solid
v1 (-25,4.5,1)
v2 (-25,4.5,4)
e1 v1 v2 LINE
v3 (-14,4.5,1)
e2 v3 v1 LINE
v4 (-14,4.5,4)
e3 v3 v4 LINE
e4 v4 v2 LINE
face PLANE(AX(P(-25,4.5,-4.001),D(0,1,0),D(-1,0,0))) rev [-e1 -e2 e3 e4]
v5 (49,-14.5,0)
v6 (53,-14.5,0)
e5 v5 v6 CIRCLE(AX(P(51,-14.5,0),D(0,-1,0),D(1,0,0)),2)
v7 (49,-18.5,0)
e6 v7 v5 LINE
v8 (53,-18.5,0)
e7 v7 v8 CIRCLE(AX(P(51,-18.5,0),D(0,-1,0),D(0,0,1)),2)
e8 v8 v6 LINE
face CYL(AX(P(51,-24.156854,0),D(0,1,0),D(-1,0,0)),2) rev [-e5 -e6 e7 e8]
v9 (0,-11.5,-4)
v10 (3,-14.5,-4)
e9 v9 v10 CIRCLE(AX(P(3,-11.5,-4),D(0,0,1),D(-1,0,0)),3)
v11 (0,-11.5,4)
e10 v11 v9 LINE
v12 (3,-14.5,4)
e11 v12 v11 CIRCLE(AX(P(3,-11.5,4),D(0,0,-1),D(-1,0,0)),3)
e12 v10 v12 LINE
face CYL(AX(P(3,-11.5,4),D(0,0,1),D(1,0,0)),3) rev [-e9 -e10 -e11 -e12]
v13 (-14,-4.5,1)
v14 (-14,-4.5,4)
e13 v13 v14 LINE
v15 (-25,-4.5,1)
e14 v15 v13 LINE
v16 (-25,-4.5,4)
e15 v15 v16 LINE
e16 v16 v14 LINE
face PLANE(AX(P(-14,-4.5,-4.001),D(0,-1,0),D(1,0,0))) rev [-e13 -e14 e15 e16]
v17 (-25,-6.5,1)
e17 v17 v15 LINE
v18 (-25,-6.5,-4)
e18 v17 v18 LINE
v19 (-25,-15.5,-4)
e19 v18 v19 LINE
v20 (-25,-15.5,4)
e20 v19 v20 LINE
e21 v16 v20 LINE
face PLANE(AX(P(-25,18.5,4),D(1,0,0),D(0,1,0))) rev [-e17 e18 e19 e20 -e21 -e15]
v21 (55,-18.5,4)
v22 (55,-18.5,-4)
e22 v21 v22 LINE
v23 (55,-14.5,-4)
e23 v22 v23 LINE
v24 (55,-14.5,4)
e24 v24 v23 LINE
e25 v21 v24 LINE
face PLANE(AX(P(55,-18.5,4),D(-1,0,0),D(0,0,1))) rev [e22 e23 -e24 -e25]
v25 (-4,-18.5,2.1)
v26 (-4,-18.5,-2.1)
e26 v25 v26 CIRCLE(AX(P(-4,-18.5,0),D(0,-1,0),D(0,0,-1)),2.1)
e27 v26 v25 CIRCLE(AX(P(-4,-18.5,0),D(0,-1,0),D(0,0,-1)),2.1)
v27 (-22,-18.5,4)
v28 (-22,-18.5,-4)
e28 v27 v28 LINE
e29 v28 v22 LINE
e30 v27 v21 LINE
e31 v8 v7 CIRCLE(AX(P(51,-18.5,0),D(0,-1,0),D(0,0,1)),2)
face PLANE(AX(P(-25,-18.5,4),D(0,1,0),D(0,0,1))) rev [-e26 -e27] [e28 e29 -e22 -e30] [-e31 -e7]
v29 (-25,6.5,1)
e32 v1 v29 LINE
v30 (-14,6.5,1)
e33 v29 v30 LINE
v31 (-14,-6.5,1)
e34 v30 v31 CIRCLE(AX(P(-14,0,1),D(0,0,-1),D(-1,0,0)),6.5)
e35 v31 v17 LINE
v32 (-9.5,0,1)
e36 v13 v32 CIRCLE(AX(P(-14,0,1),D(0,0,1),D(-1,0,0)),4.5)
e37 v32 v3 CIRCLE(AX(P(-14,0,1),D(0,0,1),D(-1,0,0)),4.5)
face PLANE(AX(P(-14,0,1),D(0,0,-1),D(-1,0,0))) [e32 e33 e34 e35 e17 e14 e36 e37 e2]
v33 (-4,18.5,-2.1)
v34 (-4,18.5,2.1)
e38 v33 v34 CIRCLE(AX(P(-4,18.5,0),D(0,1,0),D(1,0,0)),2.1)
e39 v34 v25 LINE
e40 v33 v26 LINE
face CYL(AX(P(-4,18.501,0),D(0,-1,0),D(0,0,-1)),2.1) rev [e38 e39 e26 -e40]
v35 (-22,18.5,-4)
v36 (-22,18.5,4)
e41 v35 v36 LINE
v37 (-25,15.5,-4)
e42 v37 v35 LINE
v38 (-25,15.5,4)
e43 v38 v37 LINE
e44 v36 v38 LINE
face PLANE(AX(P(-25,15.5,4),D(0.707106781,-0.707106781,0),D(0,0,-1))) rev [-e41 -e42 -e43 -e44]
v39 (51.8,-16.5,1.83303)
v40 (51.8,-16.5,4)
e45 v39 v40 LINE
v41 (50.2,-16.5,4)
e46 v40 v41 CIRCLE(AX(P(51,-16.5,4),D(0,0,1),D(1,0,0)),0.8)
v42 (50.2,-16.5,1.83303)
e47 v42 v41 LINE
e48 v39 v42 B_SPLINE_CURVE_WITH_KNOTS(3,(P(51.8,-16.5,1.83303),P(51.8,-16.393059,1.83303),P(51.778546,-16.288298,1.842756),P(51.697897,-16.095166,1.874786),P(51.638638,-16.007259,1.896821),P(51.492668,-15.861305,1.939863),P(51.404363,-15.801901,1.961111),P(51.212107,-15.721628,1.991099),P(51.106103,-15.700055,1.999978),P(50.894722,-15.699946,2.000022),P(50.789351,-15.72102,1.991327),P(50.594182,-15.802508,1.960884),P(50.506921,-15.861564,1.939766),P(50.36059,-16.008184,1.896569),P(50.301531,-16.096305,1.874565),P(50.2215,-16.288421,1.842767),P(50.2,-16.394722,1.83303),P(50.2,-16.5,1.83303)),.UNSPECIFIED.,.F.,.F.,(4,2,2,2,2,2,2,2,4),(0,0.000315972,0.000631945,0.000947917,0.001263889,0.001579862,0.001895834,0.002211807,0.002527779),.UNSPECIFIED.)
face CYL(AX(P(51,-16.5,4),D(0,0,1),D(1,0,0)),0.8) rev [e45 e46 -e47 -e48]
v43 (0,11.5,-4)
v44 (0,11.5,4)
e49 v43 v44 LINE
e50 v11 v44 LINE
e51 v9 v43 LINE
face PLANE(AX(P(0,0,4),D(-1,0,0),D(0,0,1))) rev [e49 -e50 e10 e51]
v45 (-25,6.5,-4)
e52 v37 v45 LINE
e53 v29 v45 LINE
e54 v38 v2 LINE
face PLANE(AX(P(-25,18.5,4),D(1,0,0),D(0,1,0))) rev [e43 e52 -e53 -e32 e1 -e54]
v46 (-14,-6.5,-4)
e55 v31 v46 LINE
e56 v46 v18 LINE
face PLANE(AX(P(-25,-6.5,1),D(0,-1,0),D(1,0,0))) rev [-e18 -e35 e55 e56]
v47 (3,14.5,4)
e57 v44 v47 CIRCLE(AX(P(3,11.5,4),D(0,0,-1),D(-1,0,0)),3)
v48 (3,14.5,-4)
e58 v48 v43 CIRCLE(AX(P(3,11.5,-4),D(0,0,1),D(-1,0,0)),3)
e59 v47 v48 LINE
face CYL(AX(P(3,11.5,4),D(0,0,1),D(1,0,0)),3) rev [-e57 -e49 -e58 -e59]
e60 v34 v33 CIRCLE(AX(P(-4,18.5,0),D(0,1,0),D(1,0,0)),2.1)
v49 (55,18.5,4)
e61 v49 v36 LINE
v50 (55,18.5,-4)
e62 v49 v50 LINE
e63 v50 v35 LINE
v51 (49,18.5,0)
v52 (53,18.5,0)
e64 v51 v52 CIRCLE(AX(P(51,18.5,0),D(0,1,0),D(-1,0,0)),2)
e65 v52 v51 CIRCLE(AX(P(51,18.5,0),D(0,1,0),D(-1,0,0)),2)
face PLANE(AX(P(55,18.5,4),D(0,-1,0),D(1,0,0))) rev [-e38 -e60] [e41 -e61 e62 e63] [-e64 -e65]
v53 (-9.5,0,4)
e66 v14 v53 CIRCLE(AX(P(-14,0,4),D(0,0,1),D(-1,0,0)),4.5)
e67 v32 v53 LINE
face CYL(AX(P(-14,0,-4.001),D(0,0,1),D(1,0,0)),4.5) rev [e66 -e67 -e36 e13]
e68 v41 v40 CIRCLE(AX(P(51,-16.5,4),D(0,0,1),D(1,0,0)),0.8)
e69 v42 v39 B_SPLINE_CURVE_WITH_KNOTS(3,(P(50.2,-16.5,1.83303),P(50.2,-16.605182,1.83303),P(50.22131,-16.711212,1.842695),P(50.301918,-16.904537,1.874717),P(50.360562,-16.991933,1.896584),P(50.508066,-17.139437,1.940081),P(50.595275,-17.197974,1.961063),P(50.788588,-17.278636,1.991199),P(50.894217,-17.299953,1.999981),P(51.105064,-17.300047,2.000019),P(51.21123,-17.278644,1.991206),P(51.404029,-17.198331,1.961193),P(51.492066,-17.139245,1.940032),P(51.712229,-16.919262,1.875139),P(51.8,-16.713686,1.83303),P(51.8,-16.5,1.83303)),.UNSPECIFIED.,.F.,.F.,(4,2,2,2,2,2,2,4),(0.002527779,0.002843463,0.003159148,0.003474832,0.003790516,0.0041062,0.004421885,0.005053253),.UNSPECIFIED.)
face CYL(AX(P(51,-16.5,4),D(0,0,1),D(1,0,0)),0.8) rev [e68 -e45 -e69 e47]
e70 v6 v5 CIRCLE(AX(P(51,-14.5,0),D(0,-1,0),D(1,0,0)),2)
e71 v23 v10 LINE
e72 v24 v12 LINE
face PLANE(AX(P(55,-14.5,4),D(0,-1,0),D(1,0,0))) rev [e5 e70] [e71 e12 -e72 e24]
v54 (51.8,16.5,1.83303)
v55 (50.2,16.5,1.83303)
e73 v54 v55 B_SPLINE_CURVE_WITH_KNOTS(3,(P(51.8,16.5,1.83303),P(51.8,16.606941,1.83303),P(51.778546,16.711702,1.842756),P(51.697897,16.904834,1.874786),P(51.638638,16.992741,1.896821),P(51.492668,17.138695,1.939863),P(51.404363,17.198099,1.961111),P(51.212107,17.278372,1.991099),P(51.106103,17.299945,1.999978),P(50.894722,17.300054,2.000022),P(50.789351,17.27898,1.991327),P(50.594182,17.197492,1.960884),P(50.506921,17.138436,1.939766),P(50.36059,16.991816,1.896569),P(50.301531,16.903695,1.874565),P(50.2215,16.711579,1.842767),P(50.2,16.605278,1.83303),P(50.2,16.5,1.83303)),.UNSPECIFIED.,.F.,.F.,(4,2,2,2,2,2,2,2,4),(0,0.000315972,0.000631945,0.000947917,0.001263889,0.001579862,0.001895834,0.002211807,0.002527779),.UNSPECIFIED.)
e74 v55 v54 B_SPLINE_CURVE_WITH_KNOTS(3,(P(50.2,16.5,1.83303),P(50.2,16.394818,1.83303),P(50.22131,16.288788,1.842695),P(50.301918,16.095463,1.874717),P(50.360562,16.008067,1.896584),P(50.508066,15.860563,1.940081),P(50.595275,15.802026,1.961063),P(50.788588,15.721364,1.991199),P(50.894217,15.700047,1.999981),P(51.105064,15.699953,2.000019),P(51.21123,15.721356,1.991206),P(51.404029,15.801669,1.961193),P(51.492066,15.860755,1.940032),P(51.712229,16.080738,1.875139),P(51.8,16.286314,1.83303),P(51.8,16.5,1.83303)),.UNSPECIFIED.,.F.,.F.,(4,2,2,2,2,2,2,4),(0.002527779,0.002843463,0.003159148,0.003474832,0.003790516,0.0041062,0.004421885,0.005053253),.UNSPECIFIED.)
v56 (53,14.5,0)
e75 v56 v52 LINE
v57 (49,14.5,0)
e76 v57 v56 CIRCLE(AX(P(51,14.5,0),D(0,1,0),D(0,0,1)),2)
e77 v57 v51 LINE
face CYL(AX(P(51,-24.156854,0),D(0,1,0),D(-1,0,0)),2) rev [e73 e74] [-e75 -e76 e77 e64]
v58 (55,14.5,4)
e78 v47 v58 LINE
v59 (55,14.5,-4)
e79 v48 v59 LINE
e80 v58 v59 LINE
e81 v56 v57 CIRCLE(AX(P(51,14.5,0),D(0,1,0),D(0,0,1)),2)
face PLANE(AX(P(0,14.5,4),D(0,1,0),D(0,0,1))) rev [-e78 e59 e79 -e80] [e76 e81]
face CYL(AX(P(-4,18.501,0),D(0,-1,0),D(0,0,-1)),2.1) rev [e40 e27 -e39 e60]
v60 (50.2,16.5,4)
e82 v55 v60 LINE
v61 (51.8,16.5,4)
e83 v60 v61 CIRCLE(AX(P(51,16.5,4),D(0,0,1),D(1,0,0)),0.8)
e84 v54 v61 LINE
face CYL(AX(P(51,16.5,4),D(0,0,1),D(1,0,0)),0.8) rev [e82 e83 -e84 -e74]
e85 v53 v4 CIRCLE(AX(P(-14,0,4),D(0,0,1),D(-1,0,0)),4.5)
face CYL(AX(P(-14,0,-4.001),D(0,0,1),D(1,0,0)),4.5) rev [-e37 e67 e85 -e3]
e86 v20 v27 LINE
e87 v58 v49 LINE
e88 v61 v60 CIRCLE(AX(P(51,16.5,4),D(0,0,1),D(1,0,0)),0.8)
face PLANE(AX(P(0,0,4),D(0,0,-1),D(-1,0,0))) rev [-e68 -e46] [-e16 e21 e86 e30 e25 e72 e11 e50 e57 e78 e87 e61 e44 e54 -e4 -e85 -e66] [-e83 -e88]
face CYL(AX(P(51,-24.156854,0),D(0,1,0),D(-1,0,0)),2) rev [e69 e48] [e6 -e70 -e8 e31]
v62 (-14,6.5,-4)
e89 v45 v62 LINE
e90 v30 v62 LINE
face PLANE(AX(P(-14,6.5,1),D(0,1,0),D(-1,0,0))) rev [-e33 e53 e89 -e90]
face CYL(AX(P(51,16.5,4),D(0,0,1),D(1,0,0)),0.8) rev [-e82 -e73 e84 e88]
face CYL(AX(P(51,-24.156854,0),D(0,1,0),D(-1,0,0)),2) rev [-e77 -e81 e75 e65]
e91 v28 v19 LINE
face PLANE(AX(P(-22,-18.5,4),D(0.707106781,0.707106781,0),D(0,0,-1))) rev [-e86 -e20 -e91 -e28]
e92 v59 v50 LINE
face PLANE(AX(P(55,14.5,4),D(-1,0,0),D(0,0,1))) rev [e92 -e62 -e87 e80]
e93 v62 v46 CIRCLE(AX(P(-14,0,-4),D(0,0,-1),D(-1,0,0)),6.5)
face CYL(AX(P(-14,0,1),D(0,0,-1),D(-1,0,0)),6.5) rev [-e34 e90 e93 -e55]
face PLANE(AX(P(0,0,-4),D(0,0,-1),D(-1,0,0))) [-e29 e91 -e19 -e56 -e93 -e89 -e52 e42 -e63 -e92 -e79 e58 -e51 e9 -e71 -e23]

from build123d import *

# Parameters (mm, degrees)
EXTRUDE_1_DEPTH         = 4
CUT_EXTRUDE_1_REACH     = 68.408
SKETCH_2_R              = 2
CUT_EXTRUDE_2_REACH     = 68.408
SKETCH_3_R              = 2.1
HOLE_WIZARD_M2_1_REACH  = 86.054
HOLE_WIZARD_M2_1_BORE_R = 0.8
CUT_EXTRUDE_3_REACH     = 60.577
CUT_EXTRUDE_4_DEPTH     = 5
FILLET_1_R              = 3
CHAMFER_1_SIZE          = 3


with BuildPart() as part:
    # 草图1 → 凸台-拉伸1 (new, symmetric)
    with BuildSketch(Plane.XY):
        Polygon((0, 0), (0, 14.5), (55, 14.5), (55, 18.5), (-25, 18.5), (-25, -18.5), (55, -18.5), (55, -14.5), (0, -14.5), align=None)
    extrude(amount=EXTRUDE_1_DEPTH, both=True)

    # 切除-拉伸1: up to this face of the body (flat: up to its plane)
    cut_extrude_1_end = Plane(part.part.faces().sort_by_distance((15, -18.5, 0))[0])
    # 草图2 → 切除-拉伸1 (cut, up to the picked face)
    with BuildSketch(Plane(origin=(0, 18.5, 0), x_dir=(1, 0, 0), z_dir=(0, 1, 0)), mode=Mode.PRIVATE) as cut_extrude_1_sk1:
        with Locations(Location((51, 0, 0), (0, 0, 180))):
            Circle(SKETCH_2_R)
    cut_extrude_1_tool1 = split(extrude(cut_extrude_1_sk1.sketch, amount=-CUT_EXTRUDE_1_REACH, mode=Mode.PRIVATE), bisect_by=cut_extrude_1_end, keep=Keep.BOTH, mode=Mode.PRIVATE)
    add(cut_extrude_1_tool1.solids().sort_by(Axis((51, 18.5, 0), (0, -1, 0)))[0], mode=Mode.SUBTRACT)

    # 草图3 → 切除-拉伸2 (cut, up to next)
    with BuildSketch(Plane.XZ.offset(18.5), mode=Mode.PRIVATE) as cut_extrude_2_sk1:
        with Locations(Location((-4, 0, 0), (0, 0, 270))):
            Circle(SKETCH_3_R)
    cut_extrude_2_tool1 = extrude(cut_extrude_2_sk1.sketch, amount=-CUT_EXTRUDE_2_REACH, mode=Mode.PRIVATE) & part.part
    add(cut_extrude_2_tool1.solids().sort_by_distance((-4, -18.5, 0))[0], mode=Mode.SUBTRACT)

    # M2 螺纹孔1 bore (on position points) → M2 螺纹孔1 (cut, up to next)
    with BuildSketch(Plane(origin=(51, -16.5, 4), x_dir=(1, 0, 0), z_dir=(0, 0, 1)), mode=Mode.PRIVATE) as hole_wizard_m2_1_sk1:
        Circle(HOLE_WIZARD_M2_1_BORE_R)
    hole_wizard_m2_1_tool1 = extrude(hole_wizard_m2_1_sk1.sketch, amount=-HOLE_WIZARD_M2_1_REACH, mode=Mode.PRIVATE) & part.part
    hole_wizard_m2_1 = hole_wizard_m2_1_tool1.solids().sort_by_distance((51, -16.5, 4))[0]
    add(hole_wizard_m2_1, mode=Mode.SUBTRACT)

    # 镜向1: M2 螺纹孔1 across plane
    add(hole_wizard_m2_1.mirror(Plane.ZX), mode=Mode.SUBTRACT)

    # 草图5 → 切除-拉伸3 (cut, up to next)
    with BuildSketch(Plane.XY.offset(4), mode=Mode.PRIVATE) as cut_extrude_3_sk1:
        with BuildLine():
            Line((-25, 4.5), (-14, 4.5))
            ThreePointArc((-14, 4.5), (-9.5, 0), (-14, -4.5))
            Line((-14, -4.5), (-25, -4.5))
            Line((-25, -4.5), (-25, 4.5))
        make_face()
    cut_extrude_3_tool1 = extrude(cut_extrude_3_sk1.sketch, amount=-CUT_EXTRUDE_3_REACH, mode=Mode.PRIVATE) & part.part
    add(cut_extrude_3_tool1.solids().sort_by_distance((-17.698151, 0, 4))[0], mode=Mode.SUBTRACT)

    # 草图6 → 切除-拉伸4 (cut)
    with BuildSketch(Plane(origin=(0, 0, -4), x_dir=(-1, 0, 0), z_dir=(0, 0, -1))):
        with BuildLine():
            Line((25, -6.5), (25, 6.5))
            Line((25, 6.5), (14, 6.5))
            ThreePointArc((14, 6.5), (7.5, 0), (14, -6.5))
            Line((14, -6.5), (25, -6.5))
        make_face()
    extrude(amount=-CUT_EXTRUDE_4_DEPTH, mode=Mode.SUBTRACT)

    # 圆角1
    fillet_1_edges = [part.edges().sort_by_distance(p)[0] for p in [
        (0, -14.5, 0),
        (0, 14.5, 0),
    ]]
    fillet(fillet_1_edges, radius=FILLET_1_R)

    # 倒角1
    chamfer_1_edges = [part.edges().sort_by_distance(p)[0] for p in [
        (-25, -18.5, 0),
        (-25, 18.5, 0),
    ]]
    chamfer(chamfer_1_edges, length=CHAMFER_1_SIZE)


solid = part.part
